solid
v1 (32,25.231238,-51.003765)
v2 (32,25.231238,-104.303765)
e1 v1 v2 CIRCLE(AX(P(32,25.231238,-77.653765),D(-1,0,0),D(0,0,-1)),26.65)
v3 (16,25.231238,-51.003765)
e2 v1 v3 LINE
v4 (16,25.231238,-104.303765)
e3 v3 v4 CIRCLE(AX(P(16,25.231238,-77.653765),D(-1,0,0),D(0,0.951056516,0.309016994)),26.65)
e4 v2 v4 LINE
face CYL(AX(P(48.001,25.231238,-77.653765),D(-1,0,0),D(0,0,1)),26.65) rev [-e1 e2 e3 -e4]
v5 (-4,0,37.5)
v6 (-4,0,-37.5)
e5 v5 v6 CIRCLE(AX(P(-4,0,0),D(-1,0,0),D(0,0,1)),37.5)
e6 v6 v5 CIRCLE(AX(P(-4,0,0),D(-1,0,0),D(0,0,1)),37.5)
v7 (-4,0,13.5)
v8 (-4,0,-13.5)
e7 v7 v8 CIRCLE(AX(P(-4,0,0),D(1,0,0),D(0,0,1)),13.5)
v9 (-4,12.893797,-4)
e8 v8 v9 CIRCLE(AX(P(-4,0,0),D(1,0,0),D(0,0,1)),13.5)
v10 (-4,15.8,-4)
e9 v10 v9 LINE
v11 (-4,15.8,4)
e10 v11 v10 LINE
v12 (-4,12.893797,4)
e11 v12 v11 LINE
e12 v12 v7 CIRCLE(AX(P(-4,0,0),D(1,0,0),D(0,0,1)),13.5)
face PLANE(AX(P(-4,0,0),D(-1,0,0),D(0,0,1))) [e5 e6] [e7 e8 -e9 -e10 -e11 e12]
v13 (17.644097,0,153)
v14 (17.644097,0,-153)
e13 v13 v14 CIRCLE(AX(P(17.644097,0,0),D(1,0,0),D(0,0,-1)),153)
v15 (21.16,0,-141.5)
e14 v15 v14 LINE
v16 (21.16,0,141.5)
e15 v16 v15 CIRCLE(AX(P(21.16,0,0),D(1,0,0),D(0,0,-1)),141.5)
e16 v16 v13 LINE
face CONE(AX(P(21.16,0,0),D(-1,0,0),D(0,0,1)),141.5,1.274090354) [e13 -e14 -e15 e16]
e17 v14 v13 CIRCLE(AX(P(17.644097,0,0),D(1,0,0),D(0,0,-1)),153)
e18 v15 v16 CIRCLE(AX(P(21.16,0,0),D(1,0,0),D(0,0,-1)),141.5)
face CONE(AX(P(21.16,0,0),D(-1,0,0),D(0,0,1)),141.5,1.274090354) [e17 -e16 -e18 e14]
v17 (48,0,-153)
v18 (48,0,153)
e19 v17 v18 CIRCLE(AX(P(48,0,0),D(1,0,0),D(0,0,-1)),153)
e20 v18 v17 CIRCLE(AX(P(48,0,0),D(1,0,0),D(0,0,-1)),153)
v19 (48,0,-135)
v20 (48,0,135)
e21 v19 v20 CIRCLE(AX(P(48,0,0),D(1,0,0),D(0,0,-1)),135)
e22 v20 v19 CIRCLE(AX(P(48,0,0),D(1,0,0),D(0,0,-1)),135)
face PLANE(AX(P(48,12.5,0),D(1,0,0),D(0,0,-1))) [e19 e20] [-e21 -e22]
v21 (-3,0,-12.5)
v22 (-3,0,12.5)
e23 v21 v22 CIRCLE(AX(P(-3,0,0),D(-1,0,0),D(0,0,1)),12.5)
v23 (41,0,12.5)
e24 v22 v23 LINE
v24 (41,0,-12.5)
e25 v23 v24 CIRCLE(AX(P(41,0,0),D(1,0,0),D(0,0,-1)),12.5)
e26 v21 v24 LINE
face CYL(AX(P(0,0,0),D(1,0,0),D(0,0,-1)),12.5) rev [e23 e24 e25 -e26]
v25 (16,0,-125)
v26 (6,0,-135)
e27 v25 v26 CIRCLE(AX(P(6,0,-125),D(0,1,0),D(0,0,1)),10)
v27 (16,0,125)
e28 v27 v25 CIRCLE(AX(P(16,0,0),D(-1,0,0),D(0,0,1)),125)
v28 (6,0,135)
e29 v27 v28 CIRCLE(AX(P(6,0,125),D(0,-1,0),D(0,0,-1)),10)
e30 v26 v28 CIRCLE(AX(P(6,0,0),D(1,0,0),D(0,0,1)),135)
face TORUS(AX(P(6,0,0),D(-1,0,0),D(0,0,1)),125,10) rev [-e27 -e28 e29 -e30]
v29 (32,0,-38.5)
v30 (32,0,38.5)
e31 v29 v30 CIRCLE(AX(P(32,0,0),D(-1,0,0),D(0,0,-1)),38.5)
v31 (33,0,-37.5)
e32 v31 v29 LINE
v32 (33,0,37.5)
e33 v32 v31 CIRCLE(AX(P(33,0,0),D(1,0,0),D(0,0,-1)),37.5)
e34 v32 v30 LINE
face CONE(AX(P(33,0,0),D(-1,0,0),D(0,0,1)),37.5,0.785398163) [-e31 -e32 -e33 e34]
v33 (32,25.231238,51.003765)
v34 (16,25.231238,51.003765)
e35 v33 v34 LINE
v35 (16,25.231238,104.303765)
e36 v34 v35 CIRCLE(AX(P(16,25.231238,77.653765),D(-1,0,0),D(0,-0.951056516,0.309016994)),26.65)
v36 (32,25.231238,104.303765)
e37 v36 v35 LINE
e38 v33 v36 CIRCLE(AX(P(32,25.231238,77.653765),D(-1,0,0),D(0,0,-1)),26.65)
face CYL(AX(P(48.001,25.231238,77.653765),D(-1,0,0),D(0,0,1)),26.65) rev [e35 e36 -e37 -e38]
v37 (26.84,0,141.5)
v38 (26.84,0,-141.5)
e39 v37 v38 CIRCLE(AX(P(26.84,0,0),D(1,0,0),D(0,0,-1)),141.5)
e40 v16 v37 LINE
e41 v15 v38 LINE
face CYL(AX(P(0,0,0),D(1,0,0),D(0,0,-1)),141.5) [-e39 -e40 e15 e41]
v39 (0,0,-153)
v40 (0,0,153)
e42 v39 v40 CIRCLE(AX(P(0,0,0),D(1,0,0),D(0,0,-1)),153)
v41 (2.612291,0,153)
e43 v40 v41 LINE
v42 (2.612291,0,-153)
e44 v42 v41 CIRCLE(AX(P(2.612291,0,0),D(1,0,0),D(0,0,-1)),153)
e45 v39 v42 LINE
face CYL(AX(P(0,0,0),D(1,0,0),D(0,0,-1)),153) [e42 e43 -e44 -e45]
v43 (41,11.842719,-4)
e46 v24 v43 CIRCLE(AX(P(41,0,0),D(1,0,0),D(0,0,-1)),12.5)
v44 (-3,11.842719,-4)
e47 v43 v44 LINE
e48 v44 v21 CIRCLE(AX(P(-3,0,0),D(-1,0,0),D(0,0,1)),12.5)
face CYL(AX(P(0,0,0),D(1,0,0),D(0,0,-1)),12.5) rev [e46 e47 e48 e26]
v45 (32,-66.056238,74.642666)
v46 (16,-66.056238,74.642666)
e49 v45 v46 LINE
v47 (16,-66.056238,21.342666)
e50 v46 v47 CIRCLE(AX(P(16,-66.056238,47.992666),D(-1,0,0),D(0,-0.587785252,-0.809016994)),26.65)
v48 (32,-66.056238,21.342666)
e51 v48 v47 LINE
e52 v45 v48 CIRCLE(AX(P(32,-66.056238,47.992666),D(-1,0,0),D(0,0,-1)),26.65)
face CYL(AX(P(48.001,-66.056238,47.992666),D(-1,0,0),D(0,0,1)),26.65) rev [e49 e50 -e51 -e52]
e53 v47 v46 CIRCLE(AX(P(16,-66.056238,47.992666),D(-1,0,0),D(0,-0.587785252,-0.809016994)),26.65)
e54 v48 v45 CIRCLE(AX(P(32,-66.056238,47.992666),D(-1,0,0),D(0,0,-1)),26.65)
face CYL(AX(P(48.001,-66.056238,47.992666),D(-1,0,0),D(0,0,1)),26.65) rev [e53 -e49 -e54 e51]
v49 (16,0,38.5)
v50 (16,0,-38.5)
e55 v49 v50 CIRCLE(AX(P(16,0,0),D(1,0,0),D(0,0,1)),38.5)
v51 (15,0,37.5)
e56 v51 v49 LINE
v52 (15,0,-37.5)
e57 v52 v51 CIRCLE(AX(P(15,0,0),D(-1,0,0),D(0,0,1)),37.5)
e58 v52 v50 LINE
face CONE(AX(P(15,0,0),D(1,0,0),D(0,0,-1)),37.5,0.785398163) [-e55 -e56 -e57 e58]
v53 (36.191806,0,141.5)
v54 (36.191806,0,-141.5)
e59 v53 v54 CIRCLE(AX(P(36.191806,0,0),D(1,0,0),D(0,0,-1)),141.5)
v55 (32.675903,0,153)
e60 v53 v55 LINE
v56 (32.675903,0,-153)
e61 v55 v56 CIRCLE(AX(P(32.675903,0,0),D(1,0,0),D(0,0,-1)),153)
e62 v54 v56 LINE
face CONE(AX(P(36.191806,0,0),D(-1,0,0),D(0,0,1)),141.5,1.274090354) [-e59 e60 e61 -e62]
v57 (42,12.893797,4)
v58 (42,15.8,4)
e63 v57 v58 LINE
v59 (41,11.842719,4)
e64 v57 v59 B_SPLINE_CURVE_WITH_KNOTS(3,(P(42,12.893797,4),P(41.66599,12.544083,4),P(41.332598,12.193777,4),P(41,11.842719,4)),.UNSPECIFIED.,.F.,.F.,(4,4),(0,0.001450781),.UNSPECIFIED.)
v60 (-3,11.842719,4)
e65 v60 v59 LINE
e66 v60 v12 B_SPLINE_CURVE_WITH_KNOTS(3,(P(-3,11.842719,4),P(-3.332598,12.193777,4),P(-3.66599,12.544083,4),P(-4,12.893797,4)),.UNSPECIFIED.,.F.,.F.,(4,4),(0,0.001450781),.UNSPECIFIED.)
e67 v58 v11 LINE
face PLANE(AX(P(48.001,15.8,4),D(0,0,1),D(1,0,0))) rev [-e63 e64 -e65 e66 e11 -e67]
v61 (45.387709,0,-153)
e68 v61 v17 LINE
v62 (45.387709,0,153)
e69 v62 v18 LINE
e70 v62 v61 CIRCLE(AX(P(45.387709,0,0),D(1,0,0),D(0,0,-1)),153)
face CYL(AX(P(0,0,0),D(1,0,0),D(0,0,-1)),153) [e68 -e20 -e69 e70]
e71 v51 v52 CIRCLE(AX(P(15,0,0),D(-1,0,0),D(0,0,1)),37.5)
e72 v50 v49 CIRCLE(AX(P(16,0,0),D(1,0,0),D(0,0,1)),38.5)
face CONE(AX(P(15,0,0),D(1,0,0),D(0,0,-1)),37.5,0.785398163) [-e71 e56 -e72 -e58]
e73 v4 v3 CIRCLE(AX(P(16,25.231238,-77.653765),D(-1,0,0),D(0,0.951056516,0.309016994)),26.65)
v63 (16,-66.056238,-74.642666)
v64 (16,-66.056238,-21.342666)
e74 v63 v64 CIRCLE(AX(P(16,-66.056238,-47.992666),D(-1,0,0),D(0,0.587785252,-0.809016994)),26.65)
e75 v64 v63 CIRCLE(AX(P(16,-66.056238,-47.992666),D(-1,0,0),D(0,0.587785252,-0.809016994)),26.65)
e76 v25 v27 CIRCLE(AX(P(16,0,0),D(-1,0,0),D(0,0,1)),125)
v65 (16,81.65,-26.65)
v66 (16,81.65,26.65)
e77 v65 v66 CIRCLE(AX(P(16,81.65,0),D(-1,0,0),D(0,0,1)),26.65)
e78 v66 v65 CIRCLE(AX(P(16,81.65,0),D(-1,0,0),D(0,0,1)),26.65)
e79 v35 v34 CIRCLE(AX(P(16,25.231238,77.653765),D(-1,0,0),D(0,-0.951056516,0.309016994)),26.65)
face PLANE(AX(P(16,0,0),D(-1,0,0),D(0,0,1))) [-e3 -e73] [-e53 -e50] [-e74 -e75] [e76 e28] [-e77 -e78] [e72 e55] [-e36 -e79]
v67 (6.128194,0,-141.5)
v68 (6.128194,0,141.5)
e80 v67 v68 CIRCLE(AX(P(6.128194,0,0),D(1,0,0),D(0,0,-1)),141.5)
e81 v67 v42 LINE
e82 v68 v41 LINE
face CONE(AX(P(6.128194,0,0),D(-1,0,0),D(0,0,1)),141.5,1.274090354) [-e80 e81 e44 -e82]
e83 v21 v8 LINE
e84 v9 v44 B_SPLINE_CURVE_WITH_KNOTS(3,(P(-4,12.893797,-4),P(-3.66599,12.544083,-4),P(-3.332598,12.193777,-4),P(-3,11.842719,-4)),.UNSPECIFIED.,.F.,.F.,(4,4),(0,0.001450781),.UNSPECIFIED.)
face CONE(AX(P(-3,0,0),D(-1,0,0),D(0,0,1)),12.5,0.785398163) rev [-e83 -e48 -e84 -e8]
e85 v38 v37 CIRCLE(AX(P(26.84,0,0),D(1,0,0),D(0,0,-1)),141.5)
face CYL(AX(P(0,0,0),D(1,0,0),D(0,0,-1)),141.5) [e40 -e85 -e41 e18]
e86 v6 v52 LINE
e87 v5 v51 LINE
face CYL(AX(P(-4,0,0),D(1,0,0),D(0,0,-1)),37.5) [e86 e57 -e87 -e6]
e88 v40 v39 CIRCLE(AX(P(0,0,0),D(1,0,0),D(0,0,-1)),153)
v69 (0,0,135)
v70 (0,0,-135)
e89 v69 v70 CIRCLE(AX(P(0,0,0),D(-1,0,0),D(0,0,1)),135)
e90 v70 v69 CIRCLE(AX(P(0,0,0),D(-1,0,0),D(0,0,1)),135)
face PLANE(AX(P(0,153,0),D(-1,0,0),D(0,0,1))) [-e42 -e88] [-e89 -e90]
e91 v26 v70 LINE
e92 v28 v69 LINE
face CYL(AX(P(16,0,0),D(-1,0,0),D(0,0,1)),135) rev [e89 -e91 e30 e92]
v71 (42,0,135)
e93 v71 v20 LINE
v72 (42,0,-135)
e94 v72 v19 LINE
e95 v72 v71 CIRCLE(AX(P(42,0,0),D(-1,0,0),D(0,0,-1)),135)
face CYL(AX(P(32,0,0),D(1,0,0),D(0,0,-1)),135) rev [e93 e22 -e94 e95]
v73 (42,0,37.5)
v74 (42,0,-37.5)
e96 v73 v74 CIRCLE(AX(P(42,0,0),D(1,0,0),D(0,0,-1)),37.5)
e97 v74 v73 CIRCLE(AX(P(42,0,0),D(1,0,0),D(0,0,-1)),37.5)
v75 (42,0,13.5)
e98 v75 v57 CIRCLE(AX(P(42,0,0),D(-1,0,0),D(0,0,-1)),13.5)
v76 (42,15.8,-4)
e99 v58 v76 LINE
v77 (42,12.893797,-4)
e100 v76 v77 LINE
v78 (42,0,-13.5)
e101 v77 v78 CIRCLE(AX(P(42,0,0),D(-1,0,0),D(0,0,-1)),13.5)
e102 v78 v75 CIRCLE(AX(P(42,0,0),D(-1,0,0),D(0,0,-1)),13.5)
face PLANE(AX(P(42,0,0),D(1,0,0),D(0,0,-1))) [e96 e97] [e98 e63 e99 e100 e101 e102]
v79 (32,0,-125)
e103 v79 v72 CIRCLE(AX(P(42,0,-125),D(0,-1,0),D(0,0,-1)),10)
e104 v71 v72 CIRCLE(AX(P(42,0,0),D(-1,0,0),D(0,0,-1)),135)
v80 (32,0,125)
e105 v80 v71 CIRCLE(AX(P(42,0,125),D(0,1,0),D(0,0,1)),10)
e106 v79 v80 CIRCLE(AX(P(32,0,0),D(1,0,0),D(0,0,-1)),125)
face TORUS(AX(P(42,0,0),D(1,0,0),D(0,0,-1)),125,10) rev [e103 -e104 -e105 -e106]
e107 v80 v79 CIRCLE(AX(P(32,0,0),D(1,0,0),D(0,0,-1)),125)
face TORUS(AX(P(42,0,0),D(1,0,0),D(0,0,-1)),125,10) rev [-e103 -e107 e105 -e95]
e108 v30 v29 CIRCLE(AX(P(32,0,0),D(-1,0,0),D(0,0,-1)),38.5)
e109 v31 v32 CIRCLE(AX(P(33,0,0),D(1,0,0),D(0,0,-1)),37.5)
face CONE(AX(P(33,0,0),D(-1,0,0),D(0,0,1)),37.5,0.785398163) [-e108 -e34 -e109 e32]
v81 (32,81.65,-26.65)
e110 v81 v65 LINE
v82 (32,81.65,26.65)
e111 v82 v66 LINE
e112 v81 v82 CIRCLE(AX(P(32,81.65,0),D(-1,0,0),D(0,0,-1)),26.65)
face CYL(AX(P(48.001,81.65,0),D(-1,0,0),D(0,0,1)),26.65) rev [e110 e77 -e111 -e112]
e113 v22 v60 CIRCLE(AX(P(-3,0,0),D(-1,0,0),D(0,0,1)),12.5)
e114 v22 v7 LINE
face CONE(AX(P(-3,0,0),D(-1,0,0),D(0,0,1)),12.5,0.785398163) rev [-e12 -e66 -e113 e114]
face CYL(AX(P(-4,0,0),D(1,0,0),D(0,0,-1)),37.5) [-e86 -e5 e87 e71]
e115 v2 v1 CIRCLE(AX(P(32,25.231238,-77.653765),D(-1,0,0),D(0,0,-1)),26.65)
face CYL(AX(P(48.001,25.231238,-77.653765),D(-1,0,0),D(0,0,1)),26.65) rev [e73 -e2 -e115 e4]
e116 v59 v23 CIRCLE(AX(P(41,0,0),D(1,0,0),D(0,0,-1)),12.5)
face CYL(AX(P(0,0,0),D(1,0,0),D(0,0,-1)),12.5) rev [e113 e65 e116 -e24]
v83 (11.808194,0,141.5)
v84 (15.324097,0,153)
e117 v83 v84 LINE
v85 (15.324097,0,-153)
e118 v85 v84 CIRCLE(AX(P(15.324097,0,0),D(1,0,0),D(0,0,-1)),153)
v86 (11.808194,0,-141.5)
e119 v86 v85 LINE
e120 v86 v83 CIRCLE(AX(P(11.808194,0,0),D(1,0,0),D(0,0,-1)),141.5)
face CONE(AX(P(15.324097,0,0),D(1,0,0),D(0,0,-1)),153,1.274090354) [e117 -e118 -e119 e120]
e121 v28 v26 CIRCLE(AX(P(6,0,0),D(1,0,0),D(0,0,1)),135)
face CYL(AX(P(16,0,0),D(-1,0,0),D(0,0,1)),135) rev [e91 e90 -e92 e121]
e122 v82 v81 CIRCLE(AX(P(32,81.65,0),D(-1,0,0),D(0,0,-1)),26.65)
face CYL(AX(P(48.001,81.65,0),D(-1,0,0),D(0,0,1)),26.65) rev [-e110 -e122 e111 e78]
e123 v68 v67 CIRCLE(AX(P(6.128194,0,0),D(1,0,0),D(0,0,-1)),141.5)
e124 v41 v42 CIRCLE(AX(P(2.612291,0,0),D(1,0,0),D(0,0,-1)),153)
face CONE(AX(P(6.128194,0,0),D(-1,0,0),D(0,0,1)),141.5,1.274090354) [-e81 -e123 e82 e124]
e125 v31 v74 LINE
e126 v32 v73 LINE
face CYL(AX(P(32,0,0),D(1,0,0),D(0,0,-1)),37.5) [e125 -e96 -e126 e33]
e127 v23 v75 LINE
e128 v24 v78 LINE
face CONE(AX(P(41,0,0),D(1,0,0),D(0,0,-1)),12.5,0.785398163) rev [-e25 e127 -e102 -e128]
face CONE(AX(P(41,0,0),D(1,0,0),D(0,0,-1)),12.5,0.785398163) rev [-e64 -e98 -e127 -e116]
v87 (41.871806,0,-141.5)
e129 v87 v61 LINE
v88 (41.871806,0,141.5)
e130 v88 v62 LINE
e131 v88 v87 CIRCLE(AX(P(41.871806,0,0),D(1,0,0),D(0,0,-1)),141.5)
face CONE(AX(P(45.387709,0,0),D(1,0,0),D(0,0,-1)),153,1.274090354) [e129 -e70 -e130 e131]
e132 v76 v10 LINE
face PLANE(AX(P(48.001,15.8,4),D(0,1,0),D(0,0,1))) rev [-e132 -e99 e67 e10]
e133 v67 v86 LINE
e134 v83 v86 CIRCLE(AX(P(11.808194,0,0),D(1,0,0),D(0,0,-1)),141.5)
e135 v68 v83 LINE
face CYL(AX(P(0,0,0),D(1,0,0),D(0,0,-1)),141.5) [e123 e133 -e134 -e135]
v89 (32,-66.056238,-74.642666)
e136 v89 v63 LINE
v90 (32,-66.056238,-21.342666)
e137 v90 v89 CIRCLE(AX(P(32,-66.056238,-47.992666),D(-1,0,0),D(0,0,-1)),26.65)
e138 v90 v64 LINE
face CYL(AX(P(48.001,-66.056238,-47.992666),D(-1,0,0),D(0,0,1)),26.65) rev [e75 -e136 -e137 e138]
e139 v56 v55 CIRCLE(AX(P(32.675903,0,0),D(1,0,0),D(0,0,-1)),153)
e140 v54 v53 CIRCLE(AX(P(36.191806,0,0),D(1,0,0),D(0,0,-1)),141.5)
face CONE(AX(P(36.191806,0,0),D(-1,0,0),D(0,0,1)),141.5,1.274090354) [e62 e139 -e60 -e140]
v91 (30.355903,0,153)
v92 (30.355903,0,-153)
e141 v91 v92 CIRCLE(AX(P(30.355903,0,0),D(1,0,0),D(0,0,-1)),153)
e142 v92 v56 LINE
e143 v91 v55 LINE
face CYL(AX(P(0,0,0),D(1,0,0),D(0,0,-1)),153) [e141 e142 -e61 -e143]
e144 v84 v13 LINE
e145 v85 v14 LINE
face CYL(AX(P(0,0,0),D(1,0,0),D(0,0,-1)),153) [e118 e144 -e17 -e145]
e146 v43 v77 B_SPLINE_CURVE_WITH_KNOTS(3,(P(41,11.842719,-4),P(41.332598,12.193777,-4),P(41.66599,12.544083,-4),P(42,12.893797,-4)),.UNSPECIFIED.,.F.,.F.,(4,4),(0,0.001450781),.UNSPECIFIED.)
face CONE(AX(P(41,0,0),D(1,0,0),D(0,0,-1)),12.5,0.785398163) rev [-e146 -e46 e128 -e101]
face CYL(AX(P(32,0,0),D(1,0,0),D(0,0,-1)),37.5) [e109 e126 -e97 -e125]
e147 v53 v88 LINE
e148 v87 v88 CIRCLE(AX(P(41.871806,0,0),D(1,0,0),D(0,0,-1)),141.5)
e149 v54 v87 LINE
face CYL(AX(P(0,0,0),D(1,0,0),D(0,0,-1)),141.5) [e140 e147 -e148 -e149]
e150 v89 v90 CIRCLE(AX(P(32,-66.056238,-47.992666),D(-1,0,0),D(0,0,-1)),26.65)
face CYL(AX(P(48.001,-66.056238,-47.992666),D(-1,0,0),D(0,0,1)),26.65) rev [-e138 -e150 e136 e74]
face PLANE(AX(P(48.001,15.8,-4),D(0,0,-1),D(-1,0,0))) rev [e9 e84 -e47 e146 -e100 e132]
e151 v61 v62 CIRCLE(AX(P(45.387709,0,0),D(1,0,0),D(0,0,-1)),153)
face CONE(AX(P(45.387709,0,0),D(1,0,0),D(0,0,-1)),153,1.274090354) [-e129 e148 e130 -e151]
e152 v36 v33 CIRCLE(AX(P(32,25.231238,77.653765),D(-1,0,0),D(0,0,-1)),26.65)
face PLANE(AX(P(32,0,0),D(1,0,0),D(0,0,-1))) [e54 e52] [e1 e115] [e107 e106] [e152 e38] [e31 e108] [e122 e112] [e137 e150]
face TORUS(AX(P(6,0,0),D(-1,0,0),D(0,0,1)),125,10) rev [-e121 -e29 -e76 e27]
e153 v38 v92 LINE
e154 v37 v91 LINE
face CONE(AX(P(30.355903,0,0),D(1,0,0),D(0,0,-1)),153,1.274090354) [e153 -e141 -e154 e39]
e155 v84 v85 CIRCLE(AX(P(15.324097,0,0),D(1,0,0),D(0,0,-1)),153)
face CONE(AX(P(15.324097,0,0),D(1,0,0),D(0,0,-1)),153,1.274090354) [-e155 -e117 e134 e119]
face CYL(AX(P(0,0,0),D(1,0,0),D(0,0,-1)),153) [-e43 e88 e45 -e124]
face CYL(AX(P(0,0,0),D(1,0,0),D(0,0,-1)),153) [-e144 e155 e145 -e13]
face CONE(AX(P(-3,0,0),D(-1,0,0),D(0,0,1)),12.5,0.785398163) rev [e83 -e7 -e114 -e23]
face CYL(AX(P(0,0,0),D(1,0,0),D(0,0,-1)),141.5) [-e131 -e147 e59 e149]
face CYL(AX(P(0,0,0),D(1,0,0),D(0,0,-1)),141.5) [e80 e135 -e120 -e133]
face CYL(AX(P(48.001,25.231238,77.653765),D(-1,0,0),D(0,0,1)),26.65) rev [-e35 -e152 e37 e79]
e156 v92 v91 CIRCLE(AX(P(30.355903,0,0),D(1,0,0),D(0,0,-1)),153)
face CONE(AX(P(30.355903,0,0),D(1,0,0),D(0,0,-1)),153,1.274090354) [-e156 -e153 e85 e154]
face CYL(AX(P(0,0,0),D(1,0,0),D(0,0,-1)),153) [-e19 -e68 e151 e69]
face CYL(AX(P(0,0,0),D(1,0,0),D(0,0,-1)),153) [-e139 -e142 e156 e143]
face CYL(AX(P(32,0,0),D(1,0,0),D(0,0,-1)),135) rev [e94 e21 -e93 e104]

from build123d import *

# Parameters (mm, degrees)
SKETCH8_R           = 37.5
SKETCH8_R_2         = 12.5
BOSS_EXTRUDE2_DEPTH = 4
CUT_EXTRUDE5_REACH  = 224.535
SKETCH9_W           = 8
SKETCH9_H           = 6.6
CUT_EXTRUDE6_START  = -16
SKETCH10_R          = 135
SKETCH10_R_2        = 37.5
CUT_EXTRUDE6_DEPTH  = 16
SKETCH11_R          = 135
SKETCH11_R_2        = 37.5
CUT_EXTRUDE7_DEPTH  = 16
FILLET1_R           = 10
CHAMFER1_SIZE       = 1
SKETCH13_R          = 37.5
CUT_EXTRUDE9_DEPTH  = 6
CHAMFER2_SIZE       = 1
CUT_EXTRUDE8_REACH  = 220.728
SKETCH12_R          = 26.65
CIRPATTERN1_COUNT   = 5


with BuildPart() as part:
    # Sketch1 → Revolve1 (revolve)
    with BuildSketch(Plane.XY, mode=Mode.PRIVATE) as revolve1_sk:
        Polygon((6.128194326, 141.5), (2.61229149, 153), (0, 153), (0, 12.5), (48, 12.5), (48, 153), (45.38770851, 153), (41.871805674, 141.5), (36.191805674, 141.5), (32.675902837, 153), (30.355902837, 153), (26.84, 141.5), (21.16, 141.5), (17.644097163, 153), (15.324097163, 153), (11.808194326, 141.5), align=None)
    revolve(revolve1_sk.sketch.rotate(Axis((0, 0, 0), (1, 0, 0)), 270), axis=Axis((0, 0, 0), (1, 0, 0)))

    # Sketch8 → Boss-Extrude2 (add)
    with BuildSketch(Plane.ZY):
        Circle(SKETCH8_R)
        with Locations(Location((0, 0, 0), (0, 0, 180))):
            Circle(SKETCH8_R_2, mode=Mode.SUBTRACT)
    extrude(amount=BOSS_EXTRUDE2_DEPTH)

    # Sketch9 → Cut-Extrude5 (cut, up to next)
    with BuildSketch(Plane.ZY.offset(4), mode=Mode.PRIVATE) as cut_extrude5_sk1:
        with Locations((0, 12.5)):
            Rectangle(SKETCH9_W, SKETCH9_H)
    cut_extrude5_tool1 = extrude(cut_extrude5_sk1.sketch, amount=-CUT_EXTRUDE5_REACH, mode=Mode.PRIVATE) & part.part
    add(cut_extrude5_tool1.solids().sort_by_distance((-4, 12.5, 0))[0], mode=Mode.SUBTRACT)

    # Sketch10 → Cut-Extrude6 (cut)
    with BuildSketch(Plane.ZY.offset(CUT_EXTRUDE6_START)):
        Circle(SKETCH10_R)
        Circle(SKETCH10_R_2, mode=Mode.SUBTRACT)
    extrude(amount=CUT_EXTRUDE6_DEPTH, mode=Mode.SUBTRACT)

    # Sketch11 → Cut-Extrude7 (cut)
    with BuildSketch(Plane(origin=(48, 0, 0), x_dir=(0, 0, -1), z_dir=(1, 0, 0))):
        with Locations(Location((0, 0, 0), (0, 0, 180))):
            Circle(SKETCH11_R)
        with Locations(Location((0, 0, 0), (0, 0, 180))):
            Circle(SKETCH11_R_2, mode=Mode.SUBTRACT)
    extrude(amount=-CUT_EXTRUDE7_DEPTH, mode=Mode.SUBTRACT)

    # Fillet1
    fillet1_edges = [part.edges().sort_by_distance(p)[0] for p in [
        (16, 0, -135),
        (32, 0, -135),
    ]]
    fillet(fillet1_edges, radius=FILLET1_R)

    # Chamfer1
    chamfer1_edges = [part.edges().sort_by_distance(p)[0] for p in [
        (16, 0, -37.5),
        (32, 0, -37.5),
    ]]
    chamfer(chamfer1_edges, length=CHAMFER1_SIZE)

    # Sketch13 → Cut-Extrude9 (cut)
    with BuildSketch(Plane(origin=(48, 0, 0), x_dir=(0, 0, -1), z_dir=(1, 0, 0))):
        Circle(SKETCH13_R)
    extrude(amount=-CUT_EXTRUDE9_DEPTH, mode=Mode.SUBTRACT)

    # Chamfer2
    chamfer2_edges = [part.edges().sort_by_distance(p)[0] for p in [
        (-4, -12.5, 0),
        (42, -12.5, 0),
    ]]
    chamfer(chamfer2_edges, length=CHAMFER2_SIZE)

    # Sketch12 → Cut-Extrude8 (cut, up to next)
    with BuildSketch(Plane.ZY.offset(-16), mode=Mode.PRIVATE) as cut_extrude8_sk1:
        with Locations((0, 81.65)):
            Circle(SKETCH12_R)
    cut_extrude8_tool1 = extrude(cut_extrude8_sk1.sketch, amount=-CUT_EXTRUDE8_REACH, mode=Mode.PRIVATE) & part.part
    cut_extrude8 = cut_extrude8_tool1.solids().sort_by_distance((16, 81.65, 0))[0]
    add(cut_extrude8, mode=Mode.SUBTRACT)

    # CirPattern1: Cut-Extrude8 ×5 about axis
    cirpattern1_axis = Axis((0, 0, 0), (1, 0, 0))
    for i in range(1, CIRPATTERN1_COUNT):
        add(cut_extrude8.rotate(cirpattern1_axis, i * 360 / CIRPATTERN1_COUNT), mode=Mode.SUBTRACT)


solid = part.part
